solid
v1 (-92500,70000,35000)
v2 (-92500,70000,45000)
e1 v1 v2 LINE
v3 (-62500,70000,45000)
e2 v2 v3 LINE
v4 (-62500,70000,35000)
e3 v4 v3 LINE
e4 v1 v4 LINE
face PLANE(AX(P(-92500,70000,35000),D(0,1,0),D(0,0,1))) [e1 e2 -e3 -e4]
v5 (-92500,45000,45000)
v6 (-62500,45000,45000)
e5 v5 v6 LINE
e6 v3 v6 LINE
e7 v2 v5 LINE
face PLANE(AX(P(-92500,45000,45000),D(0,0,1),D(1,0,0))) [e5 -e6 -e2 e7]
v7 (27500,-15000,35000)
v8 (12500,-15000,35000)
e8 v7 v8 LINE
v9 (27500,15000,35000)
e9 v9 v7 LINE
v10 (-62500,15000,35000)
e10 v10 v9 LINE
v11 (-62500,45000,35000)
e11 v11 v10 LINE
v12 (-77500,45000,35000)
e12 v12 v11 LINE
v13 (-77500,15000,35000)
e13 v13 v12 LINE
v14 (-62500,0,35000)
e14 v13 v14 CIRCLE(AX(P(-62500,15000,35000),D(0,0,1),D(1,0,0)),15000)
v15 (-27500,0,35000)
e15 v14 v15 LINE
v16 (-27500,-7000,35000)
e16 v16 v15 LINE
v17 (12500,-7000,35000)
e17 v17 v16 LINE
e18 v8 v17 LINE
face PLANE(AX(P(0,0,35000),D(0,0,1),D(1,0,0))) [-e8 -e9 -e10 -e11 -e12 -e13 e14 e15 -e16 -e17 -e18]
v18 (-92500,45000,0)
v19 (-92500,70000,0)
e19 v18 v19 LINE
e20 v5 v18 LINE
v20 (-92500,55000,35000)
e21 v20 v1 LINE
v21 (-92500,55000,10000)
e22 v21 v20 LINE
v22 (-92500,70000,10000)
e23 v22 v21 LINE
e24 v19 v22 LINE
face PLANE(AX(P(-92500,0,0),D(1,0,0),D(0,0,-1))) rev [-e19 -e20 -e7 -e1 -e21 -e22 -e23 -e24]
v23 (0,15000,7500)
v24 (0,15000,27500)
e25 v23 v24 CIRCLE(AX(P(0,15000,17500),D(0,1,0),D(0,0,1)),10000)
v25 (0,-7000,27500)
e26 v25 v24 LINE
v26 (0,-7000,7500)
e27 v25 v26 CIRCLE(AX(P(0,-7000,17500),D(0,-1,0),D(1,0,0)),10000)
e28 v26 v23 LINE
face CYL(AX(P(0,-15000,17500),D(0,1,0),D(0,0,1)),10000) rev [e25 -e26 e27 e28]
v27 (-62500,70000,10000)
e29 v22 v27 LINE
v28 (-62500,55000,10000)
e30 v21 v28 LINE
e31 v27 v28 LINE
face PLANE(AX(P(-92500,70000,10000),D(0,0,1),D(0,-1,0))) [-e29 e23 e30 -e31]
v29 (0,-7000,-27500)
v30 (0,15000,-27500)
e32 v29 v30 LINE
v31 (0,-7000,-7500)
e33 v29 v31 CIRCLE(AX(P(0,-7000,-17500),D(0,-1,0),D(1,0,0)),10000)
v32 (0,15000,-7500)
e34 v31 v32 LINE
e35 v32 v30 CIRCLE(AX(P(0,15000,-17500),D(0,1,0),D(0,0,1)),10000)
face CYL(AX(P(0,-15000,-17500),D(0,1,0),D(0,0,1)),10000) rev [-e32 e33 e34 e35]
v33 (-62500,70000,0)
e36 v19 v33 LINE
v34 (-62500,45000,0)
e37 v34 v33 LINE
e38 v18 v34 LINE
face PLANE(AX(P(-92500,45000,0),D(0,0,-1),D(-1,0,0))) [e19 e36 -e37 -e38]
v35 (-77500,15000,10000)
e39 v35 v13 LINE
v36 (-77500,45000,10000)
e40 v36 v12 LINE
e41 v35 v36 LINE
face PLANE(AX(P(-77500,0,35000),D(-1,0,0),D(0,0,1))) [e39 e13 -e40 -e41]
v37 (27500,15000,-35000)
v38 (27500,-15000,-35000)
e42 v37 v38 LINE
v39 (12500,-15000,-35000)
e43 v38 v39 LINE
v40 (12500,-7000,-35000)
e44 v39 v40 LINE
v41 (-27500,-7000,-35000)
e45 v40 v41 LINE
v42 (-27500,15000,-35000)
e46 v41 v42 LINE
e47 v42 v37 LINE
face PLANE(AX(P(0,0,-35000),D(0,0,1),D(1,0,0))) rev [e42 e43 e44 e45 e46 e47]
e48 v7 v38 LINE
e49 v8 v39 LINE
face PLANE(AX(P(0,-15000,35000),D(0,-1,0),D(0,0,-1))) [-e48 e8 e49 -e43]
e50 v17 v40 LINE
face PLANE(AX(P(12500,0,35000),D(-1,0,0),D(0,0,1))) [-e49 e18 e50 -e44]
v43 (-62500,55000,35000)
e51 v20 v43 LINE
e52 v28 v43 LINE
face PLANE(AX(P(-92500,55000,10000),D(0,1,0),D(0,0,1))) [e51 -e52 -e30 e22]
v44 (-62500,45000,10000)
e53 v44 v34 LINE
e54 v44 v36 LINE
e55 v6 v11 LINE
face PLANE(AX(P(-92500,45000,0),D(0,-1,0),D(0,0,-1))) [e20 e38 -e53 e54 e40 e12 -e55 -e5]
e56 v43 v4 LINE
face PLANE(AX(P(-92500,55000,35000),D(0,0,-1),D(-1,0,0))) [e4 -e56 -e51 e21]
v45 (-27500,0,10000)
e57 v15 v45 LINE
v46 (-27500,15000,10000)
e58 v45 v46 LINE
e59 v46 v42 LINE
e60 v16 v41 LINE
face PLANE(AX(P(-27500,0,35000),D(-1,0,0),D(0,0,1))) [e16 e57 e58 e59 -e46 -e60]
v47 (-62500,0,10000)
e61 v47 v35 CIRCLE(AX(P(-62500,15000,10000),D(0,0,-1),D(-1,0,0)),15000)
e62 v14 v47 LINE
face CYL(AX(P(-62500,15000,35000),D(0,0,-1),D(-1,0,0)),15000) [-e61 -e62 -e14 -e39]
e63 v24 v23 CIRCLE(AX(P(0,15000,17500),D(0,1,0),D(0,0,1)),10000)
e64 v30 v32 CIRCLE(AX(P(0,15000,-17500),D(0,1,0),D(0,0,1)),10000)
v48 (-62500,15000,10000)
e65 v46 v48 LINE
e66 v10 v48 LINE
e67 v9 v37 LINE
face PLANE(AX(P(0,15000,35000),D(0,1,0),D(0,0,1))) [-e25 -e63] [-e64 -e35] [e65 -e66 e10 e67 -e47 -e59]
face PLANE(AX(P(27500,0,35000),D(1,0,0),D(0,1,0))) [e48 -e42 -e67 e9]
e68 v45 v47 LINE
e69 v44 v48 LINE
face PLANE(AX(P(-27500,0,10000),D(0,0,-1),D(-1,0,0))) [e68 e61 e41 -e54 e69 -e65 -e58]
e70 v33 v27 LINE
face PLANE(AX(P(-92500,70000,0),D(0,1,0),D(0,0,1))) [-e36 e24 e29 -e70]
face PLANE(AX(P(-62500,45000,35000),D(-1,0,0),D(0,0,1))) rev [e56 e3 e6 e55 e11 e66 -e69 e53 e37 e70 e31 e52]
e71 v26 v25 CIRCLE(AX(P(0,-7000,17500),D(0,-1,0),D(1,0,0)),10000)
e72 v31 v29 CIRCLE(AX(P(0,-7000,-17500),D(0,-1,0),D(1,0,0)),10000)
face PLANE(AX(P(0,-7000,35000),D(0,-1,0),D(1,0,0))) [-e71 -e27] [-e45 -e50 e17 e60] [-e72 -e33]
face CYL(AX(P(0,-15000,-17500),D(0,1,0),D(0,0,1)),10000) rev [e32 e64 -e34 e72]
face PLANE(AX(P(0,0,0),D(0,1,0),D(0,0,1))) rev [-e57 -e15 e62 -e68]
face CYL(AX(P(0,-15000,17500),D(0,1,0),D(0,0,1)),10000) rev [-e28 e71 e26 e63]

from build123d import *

# Parameters (mm, degrees)
BASE_PLATE_DEPTH           = 35000
UPRIGHT_ARM_SKETCH_W       = 50000
UPRIGHT_ARM_SKETCH_H       = 25000
UPRIGHT_ARM_DEPTH          = 15000
UPRIGHT_EXTENSION_SKETCH_W = 15000
UPRIGHT_EXTENSION_SKETCH_H = 25000
UPRIGHT_EXTENSION_DEPTH    = 30000
BEND_FILLET_R15_R          = 15000
FORK_HEAD_DEPTH            = 30000
MOUNTING_HOLES_SKETCH_R    = 10000
MOUNTING_HOLES_2X_20_DEPTH = 30000


with BuildPart() as part:
    # Base Plate Profile Sketch → Base Plate (new, symmetric)
    with BuildSketch(Plane.XY):
        Polygon((12500, -7000), (-27500, -7000), (-27500, 14474.109792319), (-27500, 15000), (27500, 15000), (27500, -15000), (12500, -15000), align=None)
    extrude(amount=BASE_PLATE_DEPTH, both=True)

    # Upright Arm Sketch → Upright Arm (add)
    with BuildSketch(Plane(origin=(0, 15000, 0), x_dir=(1, 0, 0), z_dir=(0, 1, 0))):
        with Locations((-52500, -22500)):
            Rectangle(UPRIGHT_ARM_SKETCH_W, UPRIGHT_ARM_SKETCH_H)
    extrude(amount=-UPRIGHT_ARM_DEPTH)

    # Upright Extension Sketch → Upright Extension (add)
    with BuildSketch(Plane(origin=(0, 15000, 0), x_dir=(1, 0, 0), z_dir=(0, 1, 0))):
        with Locations((-70000, -22500)):
            Rectangle(UPRIGHT_EXTENSION_SKETCH_W, UPRIGHT_EXTENSION_SKETCH_H)
    extrude(amount=UPRIGHT_EXTENSION_DEPTH)

    # Bend Fillet R15
    bend_fillet_r15_edges = [part.edges().sort_by_distance(p)[0] for p in [
        (-77500, 0, 22500),
    ]]
    fillet(bend_fillet_r15_edges, radius=BEND_FILLET_R15_R)

    # Fork Head Sketch → Fork Head (add)
    with BuildSketch(Plane(origin=(-62500, 0, 0), x_dir=(0, 0, -1), z_dir=(1, 0, 0))):
        Polygon((0, 45000), (-45000, 45000), (-45000, 70000), (-35000, 70000), (-35000, 55000), (-10000, 55000), (-10000, 70000), (0, 70000), align=None)
    extrude(amount=-FORK_HEAD_DEPTH)

    # Mounting Holes Sketch → Mounting Holes 2xØ20 (cut)
    with BuildSketch(Plane(origin=(0, 15000, 0), x_dir=(1, 0, 0), z_dir=(0, 1, 0))):
        with Locations(Location((0, 17500, 0), (0, 0, 270))):
            Circle(MOUNTING_HOLES_SKETCH_R)
        with Locations(Location((0, -17500, 0), (0, 0, 270))):
            Circle(MOUNTING_HOLES_SKETCH_R)
    extrude(amount=-MOUNTING_HOLES_2X_20_DEPTH, mode=Mode.SUBTRACT)


solid = part.part
